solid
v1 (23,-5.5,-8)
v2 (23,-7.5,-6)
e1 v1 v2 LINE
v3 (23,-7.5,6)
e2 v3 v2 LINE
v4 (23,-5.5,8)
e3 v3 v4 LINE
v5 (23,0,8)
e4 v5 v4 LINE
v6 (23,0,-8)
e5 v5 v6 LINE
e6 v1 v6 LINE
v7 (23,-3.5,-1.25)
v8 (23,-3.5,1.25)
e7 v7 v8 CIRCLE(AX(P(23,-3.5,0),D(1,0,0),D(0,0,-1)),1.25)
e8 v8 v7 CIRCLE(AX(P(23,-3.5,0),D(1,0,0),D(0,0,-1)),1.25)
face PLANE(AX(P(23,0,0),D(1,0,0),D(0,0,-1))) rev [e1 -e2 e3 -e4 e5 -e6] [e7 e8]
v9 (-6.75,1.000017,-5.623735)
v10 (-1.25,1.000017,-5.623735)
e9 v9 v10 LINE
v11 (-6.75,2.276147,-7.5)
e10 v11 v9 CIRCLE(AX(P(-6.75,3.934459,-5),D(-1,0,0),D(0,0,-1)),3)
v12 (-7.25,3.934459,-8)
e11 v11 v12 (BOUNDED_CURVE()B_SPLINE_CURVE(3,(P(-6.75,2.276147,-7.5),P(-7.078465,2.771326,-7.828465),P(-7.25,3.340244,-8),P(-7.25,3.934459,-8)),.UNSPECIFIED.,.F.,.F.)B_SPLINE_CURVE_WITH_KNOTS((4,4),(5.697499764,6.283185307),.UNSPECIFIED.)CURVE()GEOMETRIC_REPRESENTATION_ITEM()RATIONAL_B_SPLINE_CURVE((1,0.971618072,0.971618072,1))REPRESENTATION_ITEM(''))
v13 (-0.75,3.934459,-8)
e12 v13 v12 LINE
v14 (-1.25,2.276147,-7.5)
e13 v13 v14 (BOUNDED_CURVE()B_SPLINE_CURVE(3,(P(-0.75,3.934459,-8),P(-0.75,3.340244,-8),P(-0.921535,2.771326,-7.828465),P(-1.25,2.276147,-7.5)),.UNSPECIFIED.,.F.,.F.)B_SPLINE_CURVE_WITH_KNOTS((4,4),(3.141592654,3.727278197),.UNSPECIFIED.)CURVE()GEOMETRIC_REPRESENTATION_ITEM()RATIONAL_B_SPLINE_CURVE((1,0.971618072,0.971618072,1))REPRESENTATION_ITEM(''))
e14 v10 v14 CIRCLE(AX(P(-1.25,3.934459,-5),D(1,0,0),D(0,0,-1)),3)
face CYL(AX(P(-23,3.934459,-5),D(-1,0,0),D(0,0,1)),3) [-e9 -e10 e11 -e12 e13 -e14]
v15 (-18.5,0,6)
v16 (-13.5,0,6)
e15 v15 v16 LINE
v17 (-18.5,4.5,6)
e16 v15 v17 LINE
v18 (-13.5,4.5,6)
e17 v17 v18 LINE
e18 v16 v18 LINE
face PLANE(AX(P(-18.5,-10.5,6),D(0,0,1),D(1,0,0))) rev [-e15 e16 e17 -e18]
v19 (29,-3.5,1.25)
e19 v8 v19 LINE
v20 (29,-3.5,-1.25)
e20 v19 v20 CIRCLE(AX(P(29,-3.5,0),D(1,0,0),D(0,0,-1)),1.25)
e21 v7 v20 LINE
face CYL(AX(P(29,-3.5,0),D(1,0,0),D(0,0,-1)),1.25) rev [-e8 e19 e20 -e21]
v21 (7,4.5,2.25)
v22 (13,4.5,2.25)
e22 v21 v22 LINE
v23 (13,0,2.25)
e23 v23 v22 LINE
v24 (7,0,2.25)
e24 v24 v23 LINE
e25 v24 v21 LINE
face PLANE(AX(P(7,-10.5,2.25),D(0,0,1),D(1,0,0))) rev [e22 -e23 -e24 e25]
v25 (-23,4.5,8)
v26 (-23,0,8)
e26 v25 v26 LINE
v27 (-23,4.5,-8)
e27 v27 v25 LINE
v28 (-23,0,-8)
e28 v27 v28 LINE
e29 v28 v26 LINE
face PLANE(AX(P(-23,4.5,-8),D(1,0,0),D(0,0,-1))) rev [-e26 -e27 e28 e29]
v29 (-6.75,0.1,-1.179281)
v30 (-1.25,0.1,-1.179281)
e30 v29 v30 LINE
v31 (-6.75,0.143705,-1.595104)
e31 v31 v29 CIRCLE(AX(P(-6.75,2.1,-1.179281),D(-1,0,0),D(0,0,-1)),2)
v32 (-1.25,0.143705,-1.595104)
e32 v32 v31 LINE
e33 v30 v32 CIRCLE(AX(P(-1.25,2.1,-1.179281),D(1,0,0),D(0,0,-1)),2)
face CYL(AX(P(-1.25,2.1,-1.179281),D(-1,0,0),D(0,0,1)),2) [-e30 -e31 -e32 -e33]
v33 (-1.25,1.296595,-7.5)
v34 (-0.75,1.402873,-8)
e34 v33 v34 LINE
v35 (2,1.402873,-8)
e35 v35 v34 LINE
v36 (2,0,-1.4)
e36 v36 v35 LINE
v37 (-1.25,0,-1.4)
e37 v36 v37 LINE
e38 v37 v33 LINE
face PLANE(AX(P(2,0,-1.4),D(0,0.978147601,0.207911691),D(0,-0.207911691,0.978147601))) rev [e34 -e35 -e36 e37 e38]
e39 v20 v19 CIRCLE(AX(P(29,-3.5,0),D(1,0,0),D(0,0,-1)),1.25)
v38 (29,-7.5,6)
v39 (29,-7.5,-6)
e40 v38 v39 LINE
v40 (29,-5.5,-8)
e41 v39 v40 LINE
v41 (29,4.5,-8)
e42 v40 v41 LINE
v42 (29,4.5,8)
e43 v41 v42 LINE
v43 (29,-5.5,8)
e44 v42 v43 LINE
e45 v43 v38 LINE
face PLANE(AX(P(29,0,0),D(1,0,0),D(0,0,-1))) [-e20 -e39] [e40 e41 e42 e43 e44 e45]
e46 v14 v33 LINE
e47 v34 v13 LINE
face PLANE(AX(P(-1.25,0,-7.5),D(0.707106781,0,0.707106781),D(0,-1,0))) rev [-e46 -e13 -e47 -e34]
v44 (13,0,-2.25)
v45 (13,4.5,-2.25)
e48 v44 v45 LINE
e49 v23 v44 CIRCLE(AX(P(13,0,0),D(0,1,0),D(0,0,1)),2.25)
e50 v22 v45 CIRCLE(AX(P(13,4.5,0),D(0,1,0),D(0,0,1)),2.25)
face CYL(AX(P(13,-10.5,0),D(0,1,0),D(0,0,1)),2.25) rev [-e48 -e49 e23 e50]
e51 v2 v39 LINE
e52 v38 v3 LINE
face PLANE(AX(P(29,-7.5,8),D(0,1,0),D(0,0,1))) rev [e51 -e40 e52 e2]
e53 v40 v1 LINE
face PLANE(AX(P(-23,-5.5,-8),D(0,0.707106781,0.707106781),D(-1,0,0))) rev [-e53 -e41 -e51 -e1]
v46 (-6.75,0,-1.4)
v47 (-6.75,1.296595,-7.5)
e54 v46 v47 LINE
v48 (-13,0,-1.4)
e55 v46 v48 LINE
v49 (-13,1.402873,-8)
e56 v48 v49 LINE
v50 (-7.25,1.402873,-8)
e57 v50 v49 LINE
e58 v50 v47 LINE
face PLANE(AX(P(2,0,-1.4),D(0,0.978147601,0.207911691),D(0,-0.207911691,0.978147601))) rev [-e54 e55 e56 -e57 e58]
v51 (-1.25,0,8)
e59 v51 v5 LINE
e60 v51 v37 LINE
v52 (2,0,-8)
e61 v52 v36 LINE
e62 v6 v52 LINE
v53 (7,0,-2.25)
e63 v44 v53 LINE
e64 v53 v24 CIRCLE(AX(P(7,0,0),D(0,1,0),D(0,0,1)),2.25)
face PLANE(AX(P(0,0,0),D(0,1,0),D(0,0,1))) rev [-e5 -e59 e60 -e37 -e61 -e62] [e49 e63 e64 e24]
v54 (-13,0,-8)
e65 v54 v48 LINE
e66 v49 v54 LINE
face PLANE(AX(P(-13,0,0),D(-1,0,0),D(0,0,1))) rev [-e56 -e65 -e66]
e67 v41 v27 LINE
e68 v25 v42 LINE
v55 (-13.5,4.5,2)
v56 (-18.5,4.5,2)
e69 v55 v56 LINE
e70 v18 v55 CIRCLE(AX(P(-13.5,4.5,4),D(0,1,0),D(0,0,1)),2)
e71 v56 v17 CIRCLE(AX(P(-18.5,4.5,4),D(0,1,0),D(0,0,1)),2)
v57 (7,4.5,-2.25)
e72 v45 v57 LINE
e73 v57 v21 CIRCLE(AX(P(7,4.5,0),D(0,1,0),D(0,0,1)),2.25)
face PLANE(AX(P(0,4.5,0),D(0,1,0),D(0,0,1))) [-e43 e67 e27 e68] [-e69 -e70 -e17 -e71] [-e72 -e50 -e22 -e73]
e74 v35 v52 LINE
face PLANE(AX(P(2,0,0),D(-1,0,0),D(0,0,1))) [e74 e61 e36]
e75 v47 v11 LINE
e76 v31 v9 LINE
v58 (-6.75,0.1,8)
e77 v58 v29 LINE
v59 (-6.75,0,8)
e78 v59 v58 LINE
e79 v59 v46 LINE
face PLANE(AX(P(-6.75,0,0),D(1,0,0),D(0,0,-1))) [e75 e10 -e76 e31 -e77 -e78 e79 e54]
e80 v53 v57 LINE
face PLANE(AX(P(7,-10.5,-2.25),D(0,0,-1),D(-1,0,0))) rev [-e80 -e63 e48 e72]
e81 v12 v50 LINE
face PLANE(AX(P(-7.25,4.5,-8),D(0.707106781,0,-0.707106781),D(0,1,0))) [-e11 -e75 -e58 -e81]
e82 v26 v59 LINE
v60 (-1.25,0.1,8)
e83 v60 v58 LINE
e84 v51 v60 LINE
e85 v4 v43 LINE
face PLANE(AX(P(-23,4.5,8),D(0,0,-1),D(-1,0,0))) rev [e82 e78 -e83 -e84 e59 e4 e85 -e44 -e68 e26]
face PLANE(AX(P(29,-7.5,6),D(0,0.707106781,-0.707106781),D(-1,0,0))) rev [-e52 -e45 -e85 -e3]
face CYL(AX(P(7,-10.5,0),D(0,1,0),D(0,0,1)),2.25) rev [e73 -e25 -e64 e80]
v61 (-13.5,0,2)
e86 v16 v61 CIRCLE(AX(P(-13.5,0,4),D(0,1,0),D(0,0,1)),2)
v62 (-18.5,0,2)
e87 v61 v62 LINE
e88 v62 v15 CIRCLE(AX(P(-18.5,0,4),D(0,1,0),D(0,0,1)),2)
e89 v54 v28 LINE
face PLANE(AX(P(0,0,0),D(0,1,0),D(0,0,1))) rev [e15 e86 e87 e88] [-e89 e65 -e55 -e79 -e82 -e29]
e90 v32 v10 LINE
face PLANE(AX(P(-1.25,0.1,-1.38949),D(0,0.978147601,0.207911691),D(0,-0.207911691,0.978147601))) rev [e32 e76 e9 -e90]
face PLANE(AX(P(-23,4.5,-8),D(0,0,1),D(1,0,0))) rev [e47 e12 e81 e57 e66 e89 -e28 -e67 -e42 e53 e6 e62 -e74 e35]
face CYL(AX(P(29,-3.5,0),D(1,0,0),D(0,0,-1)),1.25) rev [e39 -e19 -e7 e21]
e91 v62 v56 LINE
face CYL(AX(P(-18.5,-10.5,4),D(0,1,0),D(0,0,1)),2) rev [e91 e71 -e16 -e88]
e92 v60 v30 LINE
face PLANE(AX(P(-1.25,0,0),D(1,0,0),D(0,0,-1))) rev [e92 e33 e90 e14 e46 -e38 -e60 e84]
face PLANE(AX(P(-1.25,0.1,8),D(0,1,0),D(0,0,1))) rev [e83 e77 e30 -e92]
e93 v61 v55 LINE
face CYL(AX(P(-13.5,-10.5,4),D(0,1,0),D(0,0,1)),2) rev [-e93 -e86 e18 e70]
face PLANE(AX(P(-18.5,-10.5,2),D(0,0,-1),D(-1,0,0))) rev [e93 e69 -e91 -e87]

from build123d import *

# Parameters (mm, degrees)
SKETCH1_W             = 46
SKETCH1_H             = 16
BOSS_EXTRUDE1_DEPTH   = 4.5
SKETCH2_W             = 16
SKETCH2_H             = 12
BOSS_EXTRUDE2_DEPTH   = 6
SKETCH3_R             = 1
CUT_EXTRUDE1_DEPTH    = 10
M3_TAPPED_HOLE1_D     = 2.5
M3_TAPPED_HOLE1_DEPTH = 7.5
M3_TAPPED_HOLE1_TIP   = 0.751075774
CHAMFER1_SIZE         = 2
CUT_EXTRUDE2_DEPTH    = 7.5
CUT_EXTRUDE3_DEPTH    = 2.75
FILLET1_R             = 3
FILLET2_R             = 2
CUT_EXTRUDE4_DEPTH    = 15
CUT_EXTRUDE5_DEPTH    = 15
CHAMFER2_SIZE         = 0.5


with BuildPart() as part:
    # Sketch1 → Boss-Extrude1 (new body)
    with BuildSketch(Plane(origin=(0, 0, 0), x_dir=(1, 0, 0), z_dir=(0, 1, 0))):
        Rectangle(SKETCH1_W, SKETCH1_H)
    extrude(amount=BOSS_EXTRUDE1_DEPTH)

    # Sketch2 → Boss-Extrude2 (add)
    with BuildSketch(Plane(origin=(23, 0, 0), x_dir=(0, 0, -1), z_dir=(1, 0, 0))):
        with Locations((0, -1.5)):
            Rectangle(SKETCH2_W, SKETCH2_H)
    extrude(amount=BOSS_EXTRUDE2_DEPTH)

    # Sketch3 → Cut-Extrude1 (cut)
    with BuildSketch(Plane(origin=(29, 0, 0), x_dir=(0, 0, -1), z_dir=(1, 0, 0))):
        with Locations((0, -3.5)):
            Circle(SKETCH3_R)
    extrude(amount=-CUT_EXTRUDE1_DEPTH, mode=Mode.SUBTRACT)

    # M3 Tapped Hole1
    with Locations(Plane(origin=(29, -3.5, 0), x_dir=(0, 0, 1), z_dir=(1, 0, 0))):
        with Locations((0, 0)):
            Hole(M3_TAPPED_HOLE1_D / 2, depth=M3_TAPPED_HOLE1_DEPTH)
            with Locations((0, 0, -(M3_TAPPED_HOLE1_DEPTH + M3_TAPPED_HOLE1_TIP / 2))):  # 118° drill point
                Cone(0, M3_TAPPED_HOLE1_D / 2, M3_TAPPED_HOLE1_TIP, mode=Mode.SUBTRACT)

    # Chamfer1
    chamfer1_edges = [part.edges().sort_by_distance(p)[0] for p in [
        (26, -7.5, -8),
        (26, -7.5, 8),
    ]]
    chamfer(chamfer1_edges, length=CHAMFER1_SIZE)

    # Sketch5 → Cut-Extrude2 (cut, symmetric)
    with BuildSketch(Plane.ZY.offset(5.5)):
        Polygon((-1.4, 0), (-15.004762523, 0), (-15.004762523, 2.891781544), align=None)
    extrude(amount=CUT_EXTRUDE2_DEPTH, both=True, mode=Mode.SUBTRACT)

    # Sketch6 → Cut-Extrude3 (cut, symmetric)
    with BuildSketch(Plane.ZY.offset(4)):
        Polygon((-1.389489576, 0.1), (-8, 1.505107367), (-8, -0.5), (8, -0.5), (8, 0.1), align=None)
    extrude(amount=CUT_EXTRUDE3_DEPTH, both=True, mode=Mode.SUBTRACT)

    # Fillet1
    fillet1_edges = [part.edges().sort_by_distance(p)[0] for p in [
        (-4, 1.505107367, -8),
    ]]
    fillet(fillet1_edges, radius=FILLET1_R)

    # Fillet2
    fillet2_edges = [part.edges().sort_by_distance(p)[0] for p in [
        (-4, 0.1, -1.389489576),
    ]]
    fillet(fillet2_edges, radius=FILLET2_R)

    # Sketch7 → Cut-Extrude4 (cut)
    with BuildSketch(Plane(origin=(0, 4.5, 0), x_dir=(1, 0, 0), z_dir=(0, 1, 0))):
        with BuildLine():
            Line((-18.5, -2), (-13.5, -2))
            ThreePointArc((-13.5, -2), (-11.5, -4), (-13.5, -6))
            Line((-13.5, -6), (-18.5, -6))
            ThreePointArc((-18.5, -6), (-20.5, -4), (-18.5, -2))
        make_face()
    extrude(amount=-CUT_EXTRUDE4_DEPTH, mode=Mode.SUBTRACT)

    # Sketch8 → Cut-Extrude5 (cut)
    with BuildSketch(Plane(origin=(0, 4.5, 0), x_dir=(1, 0, 0), z_dir=(0, 1, 0))):
        with BuildLine():
            Line((7, 2.25), (13, 2.25))
            ThreePointArc((13, 2.25), (15.25, 0), (13, -2.25))
            Line((13, -2.25), (7, -2.25))
            ThreePointArc((7, -2.25), (4.75, 0), (7, 2.25))
        make_face()
    extrude(amount=-CUT_EXTRUDE5_DEPTH, mode=Mode.SUBTRACT)

    # Chamfer2
    chamfer2_edges = [part.edges().sort_by_distance(p)[0] for p in [
        (-1.25, 2.668666387, -8),
        (-6.75, 2.668666387, -8),
    ]]
    chamfer(chamfer2_edges, length=CHAMFER2_SIZE)


solid = part.part
